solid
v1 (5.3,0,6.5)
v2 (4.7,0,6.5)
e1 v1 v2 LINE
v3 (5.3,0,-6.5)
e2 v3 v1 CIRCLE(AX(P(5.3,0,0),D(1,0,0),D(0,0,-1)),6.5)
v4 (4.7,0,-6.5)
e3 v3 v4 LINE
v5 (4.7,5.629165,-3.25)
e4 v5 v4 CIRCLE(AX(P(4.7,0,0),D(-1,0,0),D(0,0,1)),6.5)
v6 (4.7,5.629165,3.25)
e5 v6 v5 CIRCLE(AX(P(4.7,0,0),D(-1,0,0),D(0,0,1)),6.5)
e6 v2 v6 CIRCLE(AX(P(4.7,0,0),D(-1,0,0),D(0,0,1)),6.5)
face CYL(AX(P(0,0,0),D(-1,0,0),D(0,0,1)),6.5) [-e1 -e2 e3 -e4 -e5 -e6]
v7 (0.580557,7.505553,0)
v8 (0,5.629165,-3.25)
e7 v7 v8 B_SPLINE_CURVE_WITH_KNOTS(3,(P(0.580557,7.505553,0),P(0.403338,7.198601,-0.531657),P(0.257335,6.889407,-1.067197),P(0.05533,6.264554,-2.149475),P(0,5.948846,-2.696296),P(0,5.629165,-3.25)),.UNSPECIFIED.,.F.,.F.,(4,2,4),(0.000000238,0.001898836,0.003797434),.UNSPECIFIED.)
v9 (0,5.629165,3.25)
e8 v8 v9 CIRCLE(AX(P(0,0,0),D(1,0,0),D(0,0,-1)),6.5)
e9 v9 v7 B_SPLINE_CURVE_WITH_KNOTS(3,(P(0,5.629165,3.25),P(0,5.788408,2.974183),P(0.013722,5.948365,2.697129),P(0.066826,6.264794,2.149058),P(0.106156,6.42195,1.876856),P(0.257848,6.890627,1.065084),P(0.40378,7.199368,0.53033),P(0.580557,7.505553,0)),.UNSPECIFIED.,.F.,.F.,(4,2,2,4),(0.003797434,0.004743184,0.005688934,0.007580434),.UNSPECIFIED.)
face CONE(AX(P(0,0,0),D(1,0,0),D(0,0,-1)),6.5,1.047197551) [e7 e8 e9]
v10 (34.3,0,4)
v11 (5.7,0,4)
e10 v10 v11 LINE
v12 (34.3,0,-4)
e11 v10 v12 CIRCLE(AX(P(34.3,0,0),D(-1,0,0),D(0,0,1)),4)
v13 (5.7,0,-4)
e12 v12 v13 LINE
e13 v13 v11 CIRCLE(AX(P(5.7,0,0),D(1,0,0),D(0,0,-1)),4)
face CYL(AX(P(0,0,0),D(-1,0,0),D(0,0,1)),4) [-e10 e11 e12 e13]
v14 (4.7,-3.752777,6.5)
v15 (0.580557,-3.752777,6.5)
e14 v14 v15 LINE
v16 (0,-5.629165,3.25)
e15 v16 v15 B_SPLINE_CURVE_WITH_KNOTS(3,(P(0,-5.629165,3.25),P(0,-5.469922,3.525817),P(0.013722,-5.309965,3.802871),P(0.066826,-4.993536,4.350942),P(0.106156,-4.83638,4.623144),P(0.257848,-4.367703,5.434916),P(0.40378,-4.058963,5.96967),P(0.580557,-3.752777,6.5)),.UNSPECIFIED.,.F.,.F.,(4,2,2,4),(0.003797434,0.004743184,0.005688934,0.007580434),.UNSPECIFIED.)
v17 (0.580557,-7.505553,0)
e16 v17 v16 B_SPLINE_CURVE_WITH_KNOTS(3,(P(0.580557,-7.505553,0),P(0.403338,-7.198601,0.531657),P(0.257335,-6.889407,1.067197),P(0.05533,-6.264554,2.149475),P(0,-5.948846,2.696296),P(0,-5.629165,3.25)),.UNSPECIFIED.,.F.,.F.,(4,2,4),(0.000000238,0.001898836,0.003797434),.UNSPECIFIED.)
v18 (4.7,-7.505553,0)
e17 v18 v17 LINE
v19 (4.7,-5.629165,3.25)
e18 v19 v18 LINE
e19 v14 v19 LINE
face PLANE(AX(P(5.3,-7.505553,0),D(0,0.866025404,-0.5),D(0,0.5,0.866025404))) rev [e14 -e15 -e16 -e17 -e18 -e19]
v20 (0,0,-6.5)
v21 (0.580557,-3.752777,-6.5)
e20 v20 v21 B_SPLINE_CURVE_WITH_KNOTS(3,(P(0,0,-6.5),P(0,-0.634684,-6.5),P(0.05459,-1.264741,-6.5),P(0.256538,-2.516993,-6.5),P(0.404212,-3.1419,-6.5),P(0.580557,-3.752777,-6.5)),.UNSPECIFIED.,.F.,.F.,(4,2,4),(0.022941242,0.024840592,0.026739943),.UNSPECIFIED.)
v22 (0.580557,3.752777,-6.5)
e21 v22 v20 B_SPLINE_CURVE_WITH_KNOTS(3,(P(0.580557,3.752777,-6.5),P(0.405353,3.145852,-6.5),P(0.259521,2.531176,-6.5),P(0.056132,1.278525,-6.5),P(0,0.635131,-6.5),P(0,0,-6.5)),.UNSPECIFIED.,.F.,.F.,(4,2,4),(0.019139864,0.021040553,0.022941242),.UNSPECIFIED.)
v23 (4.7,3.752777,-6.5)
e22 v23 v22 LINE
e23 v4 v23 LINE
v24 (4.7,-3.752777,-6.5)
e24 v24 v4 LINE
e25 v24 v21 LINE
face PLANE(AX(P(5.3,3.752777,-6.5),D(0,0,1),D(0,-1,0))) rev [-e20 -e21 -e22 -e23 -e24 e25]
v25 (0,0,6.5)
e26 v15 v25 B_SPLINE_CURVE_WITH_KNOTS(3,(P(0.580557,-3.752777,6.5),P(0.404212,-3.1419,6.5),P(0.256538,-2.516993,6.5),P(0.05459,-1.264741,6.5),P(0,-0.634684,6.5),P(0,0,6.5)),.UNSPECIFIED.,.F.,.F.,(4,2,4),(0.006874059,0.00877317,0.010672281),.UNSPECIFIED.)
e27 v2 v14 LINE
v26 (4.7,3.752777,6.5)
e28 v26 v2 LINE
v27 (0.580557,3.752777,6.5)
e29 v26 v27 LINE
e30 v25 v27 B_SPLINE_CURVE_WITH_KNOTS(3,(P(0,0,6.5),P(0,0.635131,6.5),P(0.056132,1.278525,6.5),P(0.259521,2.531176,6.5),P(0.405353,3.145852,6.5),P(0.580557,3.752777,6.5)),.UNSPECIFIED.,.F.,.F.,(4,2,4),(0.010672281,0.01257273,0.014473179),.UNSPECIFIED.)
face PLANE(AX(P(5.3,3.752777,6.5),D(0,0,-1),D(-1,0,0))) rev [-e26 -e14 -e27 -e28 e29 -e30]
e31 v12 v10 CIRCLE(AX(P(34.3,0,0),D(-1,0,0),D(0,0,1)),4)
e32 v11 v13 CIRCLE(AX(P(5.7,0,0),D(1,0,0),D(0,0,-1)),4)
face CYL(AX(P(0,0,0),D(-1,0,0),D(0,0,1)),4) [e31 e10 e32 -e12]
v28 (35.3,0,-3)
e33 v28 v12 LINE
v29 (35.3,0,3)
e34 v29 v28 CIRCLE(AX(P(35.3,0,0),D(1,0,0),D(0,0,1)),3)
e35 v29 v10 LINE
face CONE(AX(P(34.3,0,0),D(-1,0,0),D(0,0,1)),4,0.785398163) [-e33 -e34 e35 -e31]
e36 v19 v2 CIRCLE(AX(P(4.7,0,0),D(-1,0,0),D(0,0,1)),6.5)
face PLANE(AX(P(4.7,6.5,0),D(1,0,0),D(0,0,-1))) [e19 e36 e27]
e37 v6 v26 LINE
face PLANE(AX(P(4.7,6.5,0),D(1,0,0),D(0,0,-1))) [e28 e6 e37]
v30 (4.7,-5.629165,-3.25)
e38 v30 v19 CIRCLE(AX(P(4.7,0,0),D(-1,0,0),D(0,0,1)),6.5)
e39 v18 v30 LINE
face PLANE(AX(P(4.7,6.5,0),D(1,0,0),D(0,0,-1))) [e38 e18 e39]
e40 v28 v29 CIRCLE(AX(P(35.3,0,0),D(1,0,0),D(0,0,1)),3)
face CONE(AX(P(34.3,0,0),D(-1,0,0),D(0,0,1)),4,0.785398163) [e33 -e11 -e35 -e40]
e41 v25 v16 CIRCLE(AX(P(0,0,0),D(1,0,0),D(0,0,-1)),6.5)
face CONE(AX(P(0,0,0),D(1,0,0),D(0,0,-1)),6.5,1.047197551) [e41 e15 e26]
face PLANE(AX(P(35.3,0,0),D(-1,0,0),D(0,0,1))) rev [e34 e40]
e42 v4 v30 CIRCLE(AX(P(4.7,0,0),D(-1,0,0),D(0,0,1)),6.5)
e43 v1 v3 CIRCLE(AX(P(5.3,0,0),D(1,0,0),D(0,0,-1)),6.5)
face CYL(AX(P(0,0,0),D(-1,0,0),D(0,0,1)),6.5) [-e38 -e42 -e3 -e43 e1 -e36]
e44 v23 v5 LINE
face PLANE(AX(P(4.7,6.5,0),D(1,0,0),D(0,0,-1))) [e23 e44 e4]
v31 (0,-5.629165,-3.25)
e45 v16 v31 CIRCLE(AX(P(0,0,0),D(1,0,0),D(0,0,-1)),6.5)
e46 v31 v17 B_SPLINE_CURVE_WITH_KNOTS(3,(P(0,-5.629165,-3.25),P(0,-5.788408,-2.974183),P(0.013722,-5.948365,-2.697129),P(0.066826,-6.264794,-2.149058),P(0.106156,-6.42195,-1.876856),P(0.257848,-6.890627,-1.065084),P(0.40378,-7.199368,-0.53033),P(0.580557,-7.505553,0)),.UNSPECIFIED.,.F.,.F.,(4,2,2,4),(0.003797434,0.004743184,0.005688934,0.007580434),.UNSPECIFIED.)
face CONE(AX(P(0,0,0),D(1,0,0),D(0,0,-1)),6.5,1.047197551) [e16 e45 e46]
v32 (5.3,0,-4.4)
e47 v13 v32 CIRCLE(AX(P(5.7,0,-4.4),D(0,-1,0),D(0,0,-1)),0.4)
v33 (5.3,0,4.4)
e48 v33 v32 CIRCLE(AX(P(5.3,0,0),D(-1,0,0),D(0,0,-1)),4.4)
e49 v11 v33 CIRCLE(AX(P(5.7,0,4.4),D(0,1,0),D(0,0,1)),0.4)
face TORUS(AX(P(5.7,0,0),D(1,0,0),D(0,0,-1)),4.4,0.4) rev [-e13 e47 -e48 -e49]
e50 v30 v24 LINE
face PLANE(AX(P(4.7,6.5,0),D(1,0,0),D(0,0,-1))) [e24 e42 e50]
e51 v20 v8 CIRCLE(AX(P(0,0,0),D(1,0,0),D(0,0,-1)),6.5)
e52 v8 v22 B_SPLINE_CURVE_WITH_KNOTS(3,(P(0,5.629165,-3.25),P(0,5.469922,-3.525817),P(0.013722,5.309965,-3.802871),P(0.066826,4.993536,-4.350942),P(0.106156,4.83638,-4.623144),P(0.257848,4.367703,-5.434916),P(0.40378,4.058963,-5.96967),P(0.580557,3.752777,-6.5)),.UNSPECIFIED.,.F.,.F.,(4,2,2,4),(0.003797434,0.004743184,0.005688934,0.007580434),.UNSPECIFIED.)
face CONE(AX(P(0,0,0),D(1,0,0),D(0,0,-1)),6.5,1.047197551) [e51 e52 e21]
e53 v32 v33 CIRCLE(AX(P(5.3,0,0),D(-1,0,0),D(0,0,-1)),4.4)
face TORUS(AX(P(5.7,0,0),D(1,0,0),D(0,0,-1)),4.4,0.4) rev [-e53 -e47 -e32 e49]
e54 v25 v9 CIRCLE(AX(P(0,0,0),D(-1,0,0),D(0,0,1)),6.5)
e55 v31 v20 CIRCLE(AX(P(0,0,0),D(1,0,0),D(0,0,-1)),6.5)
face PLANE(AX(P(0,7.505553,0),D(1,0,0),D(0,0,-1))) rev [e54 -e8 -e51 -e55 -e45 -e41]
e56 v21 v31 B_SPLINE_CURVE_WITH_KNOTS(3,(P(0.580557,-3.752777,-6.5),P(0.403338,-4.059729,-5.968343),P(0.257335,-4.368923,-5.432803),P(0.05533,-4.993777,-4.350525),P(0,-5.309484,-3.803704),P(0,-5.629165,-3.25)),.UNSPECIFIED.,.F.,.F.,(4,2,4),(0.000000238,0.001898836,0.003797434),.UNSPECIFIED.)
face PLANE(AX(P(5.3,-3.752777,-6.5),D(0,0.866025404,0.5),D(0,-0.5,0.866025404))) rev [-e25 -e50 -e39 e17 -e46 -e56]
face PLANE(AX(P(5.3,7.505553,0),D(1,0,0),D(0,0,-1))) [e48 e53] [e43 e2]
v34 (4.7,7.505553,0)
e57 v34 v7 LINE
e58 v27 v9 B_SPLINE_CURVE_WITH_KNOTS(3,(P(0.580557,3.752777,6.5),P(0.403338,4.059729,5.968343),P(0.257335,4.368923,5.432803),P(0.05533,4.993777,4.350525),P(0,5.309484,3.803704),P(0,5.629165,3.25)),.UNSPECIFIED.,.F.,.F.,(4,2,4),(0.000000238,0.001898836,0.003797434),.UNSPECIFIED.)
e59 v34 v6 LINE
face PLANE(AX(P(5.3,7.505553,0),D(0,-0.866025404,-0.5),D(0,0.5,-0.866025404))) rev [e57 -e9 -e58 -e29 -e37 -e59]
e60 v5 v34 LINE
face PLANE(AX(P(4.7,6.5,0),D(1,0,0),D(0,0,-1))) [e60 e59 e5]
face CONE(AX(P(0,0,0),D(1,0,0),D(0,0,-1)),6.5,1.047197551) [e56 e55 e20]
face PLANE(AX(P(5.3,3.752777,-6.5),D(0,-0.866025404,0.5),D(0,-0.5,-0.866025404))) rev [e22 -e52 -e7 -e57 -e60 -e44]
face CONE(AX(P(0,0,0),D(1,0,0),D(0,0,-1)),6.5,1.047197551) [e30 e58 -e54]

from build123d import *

# Parameters (mm, degrees)
EXTRUDE_368_DEPTH = 5.3
SKETCH_4_W        = 0.6
SKETCH_4_H        = 11.005553499
CHAMFER_1891_SIZE = 1
FILLET_1936_R     = 0.4


with BuildPart() as part:
    # 草图1 → Extrude 368 (new body)
    with BuildSketch(Plane(origin=(0, 0, 0), x_dir=(0, 0, -1), z_dir=(1, 0, 0))):
        Polygon((6.5, 3.75277675), (6.5, -3.75277675), (0, -7.505553499), (-6.5, -3.75277675), (-6.5, 3.75277675), (0, 7.505553499), align=None)
    extrude(amount=EXTRUDE_368_DEPTH)

    # 草图2 → 凸台-旋转1 (revolve)
    with BuildSketch(Plane.XY, mode=Mode.PRIVATE) as revolve_1_sk:
        Polygon((0, 0), (35.3, 0), (35.3, 2.9175), (35.3, 4), (0, 4), align=None)
    revolve(revolve_1_sk.sketch.rotate(Axis((0, 0, 0), (1, 0, 0)), 90), axis=Axis((0, 0, 0), (1, 0, 0)))

    # 草图3 → 切除-旋转1 (revolve, cut)
    with BuildSketch(Plane.XY):
        Polygon((0, 6.5), (3.46730793, 12.505553499), (3.46730793, 17.505553499), (-10, 17.505553499), (-10, 6.5), align=None)
    revolve(axis=Axis((0, 0, 0), (1, 0, 0)), mode=Mode.SUBTRACT)

    # 草图5 → 切除-旋转2 (revolve, cut)
    with BuildSketch(Plane.XY):
        Polygon((5.3, 6.5), (1.83269207, 12.505553499), (1.83269207, 17.505553499), (11.83269207, 17.505553499), (11.83269207, 6.5), align=None)
    revolve(axis=Axis((0, 0, 0), (1, 0, 0)), mode=Mode.SUBTRACT)

    # 草图4 → 切除-旋转3 (revolve, cut)
    with BuildSketch(Plane.XY, mode=Mode.PRIVATE) as cut_revolve_3_sk:
        with Locations((5, 12.00277675)):
            Rectangle(SKETCH_4_W, SKETCH_4_H)
    revolve(cut_revolve_3_sk.sketch.rotate(Axis((0, 0, 0), (1, 0, 0)), 270), axis=Axis((0, 0, 0), (1, 0, 0)), mode=Mode.SUBTRACT)

    # Chamfer 1891
    chamfer_1891_edges = [part.edges().sort_by_distance(p)[0] for p in [
        (35.3, 0, -4),
    ]]
    chamfer(chamfer_1891_edges, length=CHAMFER_1891_SIZE)

    # Fillet 1936
    fillet_1936_edges = [part.edges().sort_by_distance(p)[0] for p in [
        (5.3, 0, -4),
    ]]
    fillet(fillet_1936_edges, radius=FILLET_1936_R)


solid = part.part
